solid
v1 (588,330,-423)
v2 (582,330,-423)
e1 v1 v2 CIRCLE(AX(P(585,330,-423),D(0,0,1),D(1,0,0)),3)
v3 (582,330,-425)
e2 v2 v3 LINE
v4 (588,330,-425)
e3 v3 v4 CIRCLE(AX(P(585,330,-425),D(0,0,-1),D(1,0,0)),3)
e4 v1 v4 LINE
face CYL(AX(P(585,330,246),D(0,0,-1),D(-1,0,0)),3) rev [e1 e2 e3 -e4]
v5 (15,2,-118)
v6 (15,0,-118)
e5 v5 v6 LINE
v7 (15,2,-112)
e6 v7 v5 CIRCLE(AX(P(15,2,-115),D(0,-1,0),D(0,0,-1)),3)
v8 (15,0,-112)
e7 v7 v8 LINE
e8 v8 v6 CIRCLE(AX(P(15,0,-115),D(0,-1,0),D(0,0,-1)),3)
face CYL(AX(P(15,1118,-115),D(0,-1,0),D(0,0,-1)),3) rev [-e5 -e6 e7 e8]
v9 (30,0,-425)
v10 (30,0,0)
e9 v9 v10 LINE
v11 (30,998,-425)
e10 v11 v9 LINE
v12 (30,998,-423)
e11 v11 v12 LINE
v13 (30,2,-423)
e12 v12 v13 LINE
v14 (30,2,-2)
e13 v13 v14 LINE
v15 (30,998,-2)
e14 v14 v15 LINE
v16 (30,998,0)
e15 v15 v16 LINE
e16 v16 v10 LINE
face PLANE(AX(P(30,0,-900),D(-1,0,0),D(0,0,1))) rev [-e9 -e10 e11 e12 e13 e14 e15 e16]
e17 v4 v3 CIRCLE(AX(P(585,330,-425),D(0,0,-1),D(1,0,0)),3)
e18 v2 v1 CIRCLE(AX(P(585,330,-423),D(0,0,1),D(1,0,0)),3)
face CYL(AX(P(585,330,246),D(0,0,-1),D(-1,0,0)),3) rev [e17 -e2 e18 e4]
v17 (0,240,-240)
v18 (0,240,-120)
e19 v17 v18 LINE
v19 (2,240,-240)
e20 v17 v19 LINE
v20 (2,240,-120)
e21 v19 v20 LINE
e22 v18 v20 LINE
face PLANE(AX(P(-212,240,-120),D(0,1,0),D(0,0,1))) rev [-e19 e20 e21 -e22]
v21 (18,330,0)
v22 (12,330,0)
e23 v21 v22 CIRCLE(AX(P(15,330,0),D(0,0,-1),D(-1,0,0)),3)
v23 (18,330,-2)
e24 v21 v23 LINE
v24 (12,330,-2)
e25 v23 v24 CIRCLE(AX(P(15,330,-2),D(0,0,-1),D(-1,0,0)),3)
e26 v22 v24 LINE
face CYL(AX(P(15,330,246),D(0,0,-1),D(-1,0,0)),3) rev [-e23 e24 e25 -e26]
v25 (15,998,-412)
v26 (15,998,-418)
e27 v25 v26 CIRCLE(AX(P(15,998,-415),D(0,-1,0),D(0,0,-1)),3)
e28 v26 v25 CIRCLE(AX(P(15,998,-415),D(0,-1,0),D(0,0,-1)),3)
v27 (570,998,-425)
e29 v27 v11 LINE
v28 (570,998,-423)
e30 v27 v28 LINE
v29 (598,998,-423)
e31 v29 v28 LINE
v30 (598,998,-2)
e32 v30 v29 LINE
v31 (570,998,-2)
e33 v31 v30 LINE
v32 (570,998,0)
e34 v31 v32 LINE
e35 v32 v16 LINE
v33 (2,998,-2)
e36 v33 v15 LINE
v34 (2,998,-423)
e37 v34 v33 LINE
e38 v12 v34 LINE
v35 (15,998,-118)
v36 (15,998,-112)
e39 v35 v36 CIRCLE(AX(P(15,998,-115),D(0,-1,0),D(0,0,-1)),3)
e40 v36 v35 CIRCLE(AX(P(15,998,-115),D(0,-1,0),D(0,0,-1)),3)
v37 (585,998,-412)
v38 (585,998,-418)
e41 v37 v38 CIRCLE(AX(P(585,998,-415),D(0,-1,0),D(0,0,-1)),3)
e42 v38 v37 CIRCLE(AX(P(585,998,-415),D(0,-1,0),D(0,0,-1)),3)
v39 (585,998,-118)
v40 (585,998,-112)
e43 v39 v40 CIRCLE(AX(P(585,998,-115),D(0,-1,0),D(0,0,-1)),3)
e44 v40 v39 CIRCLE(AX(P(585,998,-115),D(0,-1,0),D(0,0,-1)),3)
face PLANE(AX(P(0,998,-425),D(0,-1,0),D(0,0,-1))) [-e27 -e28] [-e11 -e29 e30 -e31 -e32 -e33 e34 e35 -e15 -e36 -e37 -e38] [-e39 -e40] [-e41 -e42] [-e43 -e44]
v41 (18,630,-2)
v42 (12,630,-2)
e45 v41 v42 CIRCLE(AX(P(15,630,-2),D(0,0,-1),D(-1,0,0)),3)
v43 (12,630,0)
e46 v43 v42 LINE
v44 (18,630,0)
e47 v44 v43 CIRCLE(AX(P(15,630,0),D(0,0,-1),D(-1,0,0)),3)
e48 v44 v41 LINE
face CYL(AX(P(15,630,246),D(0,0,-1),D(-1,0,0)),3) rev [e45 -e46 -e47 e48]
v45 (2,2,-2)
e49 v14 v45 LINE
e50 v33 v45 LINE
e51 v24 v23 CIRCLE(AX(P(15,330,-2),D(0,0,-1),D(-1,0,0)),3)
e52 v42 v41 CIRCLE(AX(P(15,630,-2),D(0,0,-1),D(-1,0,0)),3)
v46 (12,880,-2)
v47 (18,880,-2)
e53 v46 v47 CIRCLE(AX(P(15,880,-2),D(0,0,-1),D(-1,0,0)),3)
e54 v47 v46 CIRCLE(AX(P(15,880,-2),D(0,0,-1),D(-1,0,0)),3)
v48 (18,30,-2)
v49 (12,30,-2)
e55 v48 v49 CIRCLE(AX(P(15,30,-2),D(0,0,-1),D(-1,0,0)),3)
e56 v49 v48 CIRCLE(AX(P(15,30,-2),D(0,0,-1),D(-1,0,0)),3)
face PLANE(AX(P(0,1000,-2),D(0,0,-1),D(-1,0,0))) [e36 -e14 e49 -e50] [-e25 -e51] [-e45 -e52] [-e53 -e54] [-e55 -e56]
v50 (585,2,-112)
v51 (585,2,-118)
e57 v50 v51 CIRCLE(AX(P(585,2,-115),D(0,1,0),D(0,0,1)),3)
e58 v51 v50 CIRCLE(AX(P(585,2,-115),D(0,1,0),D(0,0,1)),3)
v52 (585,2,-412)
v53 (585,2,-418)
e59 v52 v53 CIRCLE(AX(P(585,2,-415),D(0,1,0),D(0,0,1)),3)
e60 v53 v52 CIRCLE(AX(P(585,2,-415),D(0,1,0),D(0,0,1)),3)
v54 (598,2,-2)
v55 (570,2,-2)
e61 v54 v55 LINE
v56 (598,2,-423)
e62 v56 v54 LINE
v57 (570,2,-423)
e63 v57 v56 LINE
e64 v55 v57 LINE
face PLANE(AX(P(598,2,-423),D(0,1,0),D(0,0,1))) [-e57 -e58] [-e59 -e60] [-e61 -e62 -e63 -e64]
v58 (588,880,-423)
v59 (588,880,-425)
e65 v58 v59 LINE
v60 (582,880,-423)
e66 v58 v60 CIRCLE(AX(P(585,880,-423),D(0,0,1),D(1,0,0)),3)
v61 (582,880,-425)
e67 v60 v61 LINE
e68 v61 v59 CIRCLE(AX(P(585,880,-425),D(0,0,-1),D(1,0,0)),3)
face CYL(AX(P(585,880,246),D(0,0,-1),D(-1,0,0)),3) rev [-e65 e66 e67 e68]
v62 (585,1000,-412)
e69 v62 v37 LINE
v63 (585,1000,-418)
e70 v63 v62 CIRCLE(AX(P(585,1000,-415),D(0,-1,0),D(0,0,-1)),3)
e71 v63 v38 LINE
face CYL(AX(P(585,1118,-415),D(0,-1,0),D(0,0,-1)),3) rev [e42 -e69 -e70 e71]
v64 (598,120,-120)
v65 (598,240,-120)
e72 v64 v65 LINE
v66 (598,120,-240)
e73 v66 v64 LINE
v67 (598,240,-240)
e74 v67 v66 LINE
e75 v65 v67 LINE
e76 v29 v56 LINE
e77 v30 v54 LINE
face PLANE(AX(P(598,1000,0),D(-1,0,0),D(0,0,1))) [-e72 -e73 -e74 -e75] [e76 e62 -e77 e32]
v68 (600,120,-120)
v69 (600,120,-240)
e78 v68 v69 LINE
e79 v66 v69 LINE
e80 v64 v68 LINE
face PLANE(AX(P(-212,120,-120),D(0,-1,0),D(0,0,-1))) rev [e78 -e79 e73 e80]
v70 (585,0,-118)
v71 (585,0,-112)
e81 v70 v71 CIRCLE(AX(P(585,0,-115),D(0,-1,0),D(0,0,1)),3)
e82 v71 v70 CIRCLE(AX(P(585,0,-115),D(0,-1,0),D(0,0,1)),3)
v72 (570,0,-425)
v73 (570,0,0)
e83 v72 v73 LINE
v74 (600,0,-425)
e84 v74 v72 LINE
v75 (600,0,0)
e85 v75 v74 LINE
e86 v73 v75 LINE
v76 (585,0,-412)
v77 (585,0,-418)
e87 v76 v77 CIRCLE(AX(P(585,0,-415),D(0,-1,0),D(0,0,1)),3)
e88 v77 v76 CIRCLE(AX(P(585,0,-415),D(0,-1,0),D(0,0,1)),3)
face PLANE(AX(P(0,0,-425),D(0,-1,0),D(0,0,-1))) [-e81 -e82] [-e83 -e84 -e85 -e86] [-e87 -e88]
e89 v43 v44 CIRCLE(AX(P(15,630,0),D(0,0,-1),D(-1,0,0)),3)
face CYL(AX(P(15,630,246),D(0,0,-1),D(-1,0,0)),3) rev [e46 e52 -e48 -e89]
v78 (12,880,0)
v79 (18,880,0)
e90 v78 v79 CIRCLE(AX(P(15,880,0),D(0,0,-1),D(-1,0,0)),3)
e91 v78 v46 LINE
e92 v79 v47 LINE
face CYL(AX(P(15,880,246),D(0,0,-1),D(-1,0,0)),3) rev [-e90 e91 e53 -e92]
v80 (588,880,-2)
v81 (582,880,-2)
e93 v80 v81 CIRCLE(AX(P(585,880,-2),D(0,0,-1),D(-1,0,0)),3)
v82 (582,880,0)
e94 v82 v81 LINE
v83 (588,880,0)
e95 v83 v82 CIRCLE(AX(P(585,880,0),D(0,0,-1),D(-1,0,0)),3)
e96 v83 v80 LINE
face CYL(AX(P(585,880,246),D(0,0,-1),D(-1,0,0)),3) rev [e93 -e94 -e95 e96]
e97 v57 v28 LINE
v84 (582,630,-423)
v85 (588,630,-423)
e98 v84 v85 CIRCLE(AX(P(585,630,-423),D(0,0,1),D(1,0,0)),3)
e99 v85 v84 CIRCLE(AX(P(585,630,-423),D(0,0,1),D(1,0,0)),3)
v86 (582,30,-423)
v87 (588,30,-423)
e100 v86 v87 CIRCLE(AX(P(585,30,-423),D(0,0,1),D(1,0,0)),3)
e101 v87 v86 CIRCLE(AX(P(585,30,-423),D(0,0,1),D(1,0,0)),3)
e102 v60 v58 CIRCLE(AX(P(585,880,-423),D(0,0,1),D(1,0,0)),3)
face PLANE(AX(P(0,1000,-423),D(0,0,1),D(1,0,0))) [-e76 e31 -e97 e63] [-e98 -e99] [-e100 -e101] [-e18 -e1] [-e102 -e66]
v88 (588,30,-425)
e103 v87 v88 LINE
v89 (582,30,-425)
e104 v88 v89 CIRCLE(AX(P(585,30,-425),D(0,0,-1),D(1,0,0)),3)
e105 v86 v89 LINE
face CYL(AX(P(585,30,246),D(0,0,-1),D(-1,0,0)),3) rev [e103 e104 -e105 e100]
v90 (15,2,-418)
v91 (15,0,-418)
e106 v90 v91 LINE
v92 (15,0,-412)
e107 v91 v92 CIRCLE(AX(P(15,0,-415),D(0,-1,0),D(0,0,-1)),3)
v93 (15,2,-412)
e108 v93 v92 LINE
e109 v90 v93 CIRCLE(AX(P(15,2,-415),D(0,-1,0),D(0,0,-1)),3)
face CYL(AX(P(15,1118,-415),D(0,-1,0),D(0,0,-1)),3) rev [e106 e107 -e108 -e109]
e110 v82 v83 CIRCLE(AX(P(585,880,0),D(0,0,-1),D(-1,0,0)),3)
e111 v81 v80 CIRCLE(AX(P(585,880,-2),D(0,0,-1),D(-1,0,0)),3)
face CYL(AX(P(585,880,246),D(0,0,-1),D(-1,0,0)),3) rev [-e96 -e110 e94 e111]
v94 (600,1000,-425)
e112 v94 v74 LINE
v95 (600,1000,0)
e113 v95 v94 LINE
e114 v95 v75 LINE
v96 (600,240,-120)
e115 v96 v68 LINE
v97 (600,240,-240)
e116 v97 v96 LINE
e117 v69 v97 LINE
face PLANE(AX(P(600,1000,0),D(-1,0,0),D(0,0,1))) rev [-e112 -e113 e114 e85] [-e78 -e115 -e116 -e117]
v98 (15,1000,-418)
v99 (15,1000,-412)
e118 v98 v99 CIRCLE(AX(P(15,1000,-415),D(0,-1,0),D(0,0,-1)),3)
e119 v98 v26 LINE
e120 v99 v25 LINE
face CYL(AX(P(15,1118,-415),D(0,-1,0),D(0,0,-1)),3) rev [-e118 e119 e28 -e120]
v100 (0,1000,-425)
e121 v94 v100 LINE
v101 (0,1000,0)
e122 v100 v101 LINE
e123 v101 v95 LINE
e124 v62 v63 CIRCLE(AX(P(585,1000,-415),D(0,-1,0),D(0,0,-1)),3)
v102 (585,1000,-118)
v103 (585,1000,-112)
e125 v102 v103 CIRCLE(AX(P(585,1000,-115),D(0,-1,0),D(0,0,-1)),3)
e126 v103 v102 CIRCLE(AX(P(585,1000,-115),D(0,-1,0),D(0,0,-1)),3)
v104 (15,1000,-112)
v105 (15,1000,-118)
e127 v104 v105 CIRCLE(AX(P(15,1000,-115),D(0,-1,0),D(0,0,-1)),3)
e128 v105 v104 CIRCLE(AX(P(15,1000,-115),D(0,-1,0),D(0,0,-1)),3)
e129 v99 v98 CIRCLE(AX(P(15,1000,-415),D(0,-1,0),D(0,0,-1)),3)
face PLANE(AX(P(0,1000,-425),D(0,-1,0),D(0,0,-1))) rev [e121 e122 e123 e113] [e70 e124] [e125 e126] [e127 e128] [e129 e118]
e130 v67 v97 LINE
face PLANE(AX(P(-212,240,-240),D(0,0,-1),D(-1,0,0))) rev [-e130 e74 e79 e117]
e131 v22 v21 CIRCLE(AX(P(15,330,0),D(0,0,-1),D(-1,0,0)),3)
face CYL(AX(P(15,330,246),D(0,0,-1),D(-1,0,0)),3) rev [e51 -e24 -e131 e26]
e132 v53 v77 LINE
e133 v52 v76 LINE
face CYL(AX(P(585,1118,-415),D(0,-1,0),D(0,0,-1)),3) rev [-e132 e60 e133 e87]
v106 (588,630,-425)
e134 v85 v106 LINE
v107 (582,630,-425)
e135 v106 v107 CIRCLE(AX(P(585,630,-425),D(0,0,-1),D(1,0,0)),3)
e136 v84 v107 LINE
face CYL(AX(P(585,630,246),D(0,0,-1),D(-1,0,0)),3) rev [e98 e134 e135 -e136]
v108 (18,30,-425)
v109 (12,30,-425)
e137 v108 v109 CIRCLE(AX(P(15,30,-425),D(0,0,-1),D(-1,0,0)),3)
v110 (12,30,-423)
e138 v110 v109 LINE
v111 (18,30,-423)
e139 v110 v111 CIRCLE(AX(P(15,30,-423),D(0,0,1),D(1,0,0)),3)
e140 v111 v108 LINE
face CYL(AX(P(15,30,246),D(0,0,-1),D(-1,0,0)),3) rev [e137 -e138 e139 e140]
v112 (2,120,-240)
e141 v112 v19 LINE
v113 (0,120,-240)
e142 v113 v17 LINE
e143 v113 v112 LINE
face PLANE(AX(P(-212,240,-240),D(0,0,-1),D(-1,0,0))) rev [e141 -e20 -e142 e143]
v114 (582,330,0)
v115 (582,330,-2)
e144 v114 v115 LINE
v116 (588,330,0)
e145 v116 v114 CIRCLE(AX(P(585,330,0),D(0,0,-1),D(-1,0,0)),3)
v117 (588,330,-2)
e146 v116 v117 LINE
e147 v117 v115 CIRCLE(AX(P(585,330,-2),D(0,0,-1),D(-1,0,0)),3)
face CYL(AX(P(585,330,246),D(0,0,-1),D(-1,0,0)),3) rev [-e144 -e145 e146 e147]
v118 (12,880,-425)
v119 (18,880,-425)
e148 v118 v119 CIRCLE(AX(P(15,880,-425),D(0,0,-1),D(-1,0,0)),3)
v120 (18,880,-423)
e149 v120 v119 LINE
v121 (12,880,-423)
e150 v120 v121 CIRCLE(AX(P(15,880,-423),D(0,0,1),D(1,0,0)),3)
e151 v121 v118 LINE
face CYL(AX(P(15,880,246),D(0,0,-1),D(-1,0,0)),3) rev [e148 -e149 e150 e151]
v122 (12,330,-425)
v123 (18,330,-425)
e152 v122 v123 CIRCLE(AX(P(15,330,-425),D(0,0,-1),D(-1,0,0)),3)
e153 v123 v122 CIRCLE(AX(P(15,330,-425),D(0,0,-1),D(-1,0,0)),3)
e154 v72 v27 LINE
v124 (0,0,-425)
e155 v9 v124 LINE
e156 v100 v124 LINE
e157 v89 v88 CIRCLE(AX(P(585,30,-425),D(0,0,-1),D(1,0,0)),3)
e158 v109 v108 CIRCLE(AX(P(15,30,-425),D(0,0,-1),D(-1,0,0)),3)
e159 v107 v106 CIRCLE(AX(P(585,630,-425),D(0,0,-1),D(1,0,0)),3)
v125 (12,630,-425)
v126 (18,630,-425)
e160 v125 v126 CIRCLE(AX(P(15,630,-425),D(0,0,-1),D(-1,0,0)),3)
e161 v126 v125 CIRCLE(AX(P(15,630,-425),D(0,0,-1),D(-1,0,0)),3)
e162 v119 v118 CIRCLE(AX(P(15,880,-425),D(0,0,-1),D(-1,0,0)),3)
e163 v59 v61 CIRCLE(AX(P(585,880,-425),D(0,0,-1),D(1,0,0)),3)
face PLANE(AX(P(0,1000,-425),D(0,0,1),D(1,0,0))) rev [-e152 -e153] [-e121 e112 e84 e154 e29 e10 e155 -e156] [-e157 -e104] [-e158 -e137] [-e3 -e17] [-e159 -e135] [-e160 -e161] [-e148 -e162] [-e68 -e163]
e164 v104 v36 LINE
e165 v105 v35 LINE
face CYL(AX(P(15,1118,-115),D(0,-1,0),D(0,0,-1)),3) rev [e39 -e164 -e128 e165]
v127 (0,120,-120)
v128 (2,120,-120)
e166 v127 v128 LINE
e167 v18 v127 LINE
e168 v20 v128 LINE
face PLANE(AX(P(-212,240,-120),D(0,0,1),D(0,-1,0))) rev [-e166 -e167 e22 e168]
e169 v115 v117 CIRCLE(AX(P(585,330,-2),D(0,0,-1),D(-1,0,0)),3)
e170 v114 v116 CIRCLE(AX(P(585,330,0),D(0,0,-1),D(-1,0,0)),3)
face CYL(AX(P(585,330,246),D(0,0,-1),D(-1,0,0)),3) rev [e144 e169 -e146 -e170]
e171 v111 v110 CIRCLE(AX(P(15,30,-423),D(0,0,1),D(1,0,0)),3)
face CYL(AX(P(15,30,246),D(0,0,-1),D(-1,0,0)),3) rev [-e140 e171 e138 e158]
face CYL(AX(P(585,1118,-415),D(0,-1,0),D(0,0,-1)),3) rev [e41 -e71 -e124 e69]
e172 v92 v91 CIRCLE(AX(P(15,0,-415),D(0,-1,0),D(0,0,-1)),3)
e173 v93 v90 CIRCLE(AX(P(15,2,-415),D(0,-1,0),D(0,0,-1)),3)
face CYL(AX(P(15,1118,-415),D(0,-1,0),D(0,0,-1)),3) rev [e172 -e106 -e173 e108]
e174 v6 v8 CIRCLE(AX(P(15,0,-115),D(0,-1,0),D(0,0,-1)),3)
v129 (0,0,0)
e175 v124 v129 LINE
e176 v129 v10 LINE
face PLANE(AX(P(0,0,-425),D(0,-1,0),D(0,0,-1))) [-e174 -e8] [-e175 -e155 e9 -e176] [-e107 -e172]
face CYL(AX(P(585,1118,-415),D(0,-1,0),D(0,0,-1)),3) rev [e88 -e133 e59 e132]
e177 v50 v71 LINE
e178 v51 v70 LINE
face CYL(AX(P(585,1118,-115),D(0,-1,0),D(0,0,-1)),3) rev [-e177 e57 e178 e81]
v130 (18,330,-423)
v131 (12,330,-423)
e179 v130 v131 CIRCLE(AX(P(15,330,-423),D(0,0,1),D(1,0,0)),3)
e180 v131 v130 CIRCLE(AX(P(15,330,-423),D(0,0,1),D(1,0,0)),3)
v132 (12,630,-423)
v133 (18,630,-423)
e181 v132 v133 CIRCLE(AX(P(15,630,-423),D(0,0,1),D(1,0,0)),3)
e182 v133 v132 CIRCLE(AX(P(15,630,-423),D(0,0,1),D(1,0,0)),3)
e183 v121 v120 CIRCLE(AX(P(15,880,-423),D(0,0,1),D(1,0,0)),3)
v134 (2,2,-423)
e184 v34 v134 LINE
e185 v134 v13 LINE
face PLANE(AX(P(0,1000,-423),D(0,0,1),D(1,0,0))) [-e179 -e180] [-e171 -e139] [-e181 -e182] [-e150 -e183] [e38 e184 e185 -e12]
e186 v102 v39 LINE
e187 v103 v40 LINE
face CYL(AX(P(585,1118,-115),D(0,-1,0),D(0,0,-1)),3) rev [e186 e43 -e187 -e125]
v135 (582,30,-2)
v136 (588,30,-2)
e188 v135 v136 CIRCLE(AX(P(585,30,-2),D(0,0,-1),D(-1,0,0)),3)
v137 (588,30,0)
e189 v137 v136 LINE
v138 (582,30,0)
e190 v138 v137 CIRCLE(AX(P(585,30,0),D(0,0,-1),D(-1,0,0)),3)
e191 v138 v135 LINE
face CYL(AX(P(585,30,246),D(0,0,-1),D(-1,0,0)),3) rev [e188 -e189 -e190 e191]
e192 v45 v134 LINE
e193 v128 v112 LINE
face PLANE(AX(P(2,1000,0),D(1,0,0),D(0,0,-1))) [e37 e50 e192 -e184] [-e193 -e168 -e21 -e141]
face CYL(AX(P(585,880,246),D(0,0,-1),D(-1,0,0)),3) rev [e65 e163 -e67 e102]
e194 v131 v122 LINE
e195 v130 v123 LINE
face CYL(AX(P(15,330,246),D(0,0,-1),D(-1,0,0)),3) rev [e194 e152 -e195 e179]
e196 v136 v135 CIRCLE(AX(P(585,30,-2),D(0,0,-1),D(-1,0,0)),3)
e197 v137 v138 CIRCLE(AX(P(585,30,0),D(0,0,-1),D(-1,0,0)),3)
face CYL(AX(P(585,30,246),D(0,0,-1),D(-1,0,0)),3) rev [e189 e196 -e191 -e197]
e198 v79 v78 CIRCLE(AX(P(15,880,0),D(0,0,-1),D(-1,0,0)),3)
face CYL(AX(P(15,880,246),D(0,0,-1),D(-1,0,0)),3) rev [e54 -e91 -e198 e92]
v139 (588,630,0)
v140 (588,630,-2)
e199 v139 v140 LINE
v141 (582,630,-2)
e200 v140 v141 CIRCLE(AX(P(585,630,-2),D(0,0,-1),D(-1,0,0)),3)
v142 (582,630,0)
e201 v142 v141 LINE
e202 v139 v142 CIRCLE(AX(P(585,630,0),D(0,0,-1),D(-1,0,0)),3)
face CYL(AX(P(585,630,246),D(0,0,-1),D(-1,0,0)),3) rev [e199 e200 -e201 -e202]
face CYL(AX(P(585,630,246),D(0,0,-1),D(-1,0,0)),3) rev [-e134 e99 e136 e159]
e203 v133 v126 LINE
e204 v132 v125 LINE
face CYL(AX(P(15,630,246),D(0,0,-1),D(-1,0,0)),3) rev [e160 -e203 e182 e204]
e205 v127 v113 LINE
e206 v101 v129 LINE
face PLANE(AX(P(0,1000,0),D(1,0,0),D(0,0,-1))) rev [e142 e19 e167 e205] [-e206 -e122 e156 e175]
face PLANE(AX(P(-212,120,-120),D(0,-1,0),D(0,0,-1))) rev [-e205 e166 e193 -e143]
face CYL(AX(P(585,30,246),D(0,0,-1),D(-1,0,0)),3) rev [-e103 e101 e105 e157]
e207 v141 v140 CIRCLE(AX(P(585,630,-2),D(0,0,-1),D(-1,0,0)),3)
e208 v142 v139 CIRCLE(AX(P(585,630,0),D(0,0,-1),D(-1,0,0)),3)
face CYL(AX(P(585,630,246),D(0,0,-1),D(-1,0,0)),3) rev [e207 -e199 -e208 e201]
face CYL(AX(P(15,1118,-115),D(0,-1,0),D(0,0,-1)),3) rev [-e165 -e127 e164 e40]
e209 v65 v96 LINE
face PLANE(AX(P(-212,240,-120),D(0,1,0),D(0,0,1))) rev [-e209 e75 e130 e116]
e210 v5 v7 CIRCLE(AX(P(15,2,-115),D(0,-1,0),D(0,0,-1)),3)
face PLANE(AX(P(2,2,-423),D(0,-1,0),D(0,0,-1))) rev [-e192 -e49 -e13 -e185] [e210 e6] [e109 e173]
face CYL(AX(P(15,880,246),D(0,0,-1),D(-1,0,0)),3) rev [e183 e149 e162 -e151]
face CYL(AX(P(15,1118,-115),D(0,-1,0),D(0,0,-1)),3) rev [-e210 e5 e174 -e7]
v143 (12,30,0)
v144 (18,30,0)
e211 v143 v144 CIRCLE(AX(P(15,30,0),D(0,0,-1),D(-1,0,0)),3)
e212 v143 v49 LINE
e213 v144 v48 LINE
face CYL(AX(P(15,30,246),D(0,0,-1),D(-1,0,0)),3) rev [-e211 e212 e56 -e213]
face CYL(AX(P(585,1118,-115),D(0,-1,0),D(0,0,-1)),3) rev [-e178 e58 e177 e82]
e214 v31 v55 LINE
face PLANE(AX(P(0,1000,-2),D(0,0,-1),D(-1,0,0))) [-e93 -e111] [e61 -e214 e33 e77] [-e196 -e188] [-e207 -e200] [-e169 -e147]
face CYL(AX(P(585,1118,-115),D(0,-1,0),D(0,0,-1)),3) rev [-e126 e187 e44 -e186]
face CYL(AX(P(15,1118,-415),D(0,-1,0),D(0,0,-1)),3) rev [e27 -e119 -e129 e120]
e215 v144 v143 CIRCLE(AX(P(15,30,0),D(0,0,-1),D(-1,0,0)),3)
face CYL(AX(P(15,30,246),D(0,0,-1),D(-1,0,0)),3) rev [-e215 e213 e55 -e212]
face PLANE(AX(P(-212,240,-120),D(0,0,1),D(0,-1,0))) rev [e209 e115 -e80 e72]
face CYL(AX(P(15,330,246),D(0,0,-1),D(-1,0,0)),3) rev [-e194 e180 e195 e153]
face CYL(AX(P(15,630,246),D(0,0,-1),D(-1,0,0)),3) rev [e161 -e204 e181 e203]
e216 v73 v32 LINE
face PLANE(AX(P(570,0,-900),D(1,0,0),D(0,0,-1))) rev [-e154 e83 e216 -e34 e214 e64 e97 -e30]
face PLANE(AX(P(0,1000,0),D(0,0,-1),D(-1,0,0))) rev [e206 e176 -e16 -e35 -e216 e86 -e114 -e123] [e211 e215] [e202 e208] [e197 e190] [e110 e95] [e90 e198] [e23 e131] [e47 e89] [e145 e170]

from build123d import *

# Parameters (mm, degrees)
SKETCH_1_W          = 600
SKETCH_1_H          = 425
EXTRUDE_1_DEPTH     = 1000
SHELL_2_T           = -2
SKETCH_2_W          = 540
SKETCH_2_H          = 998
CUT_EXTRUDE_1_DEPTH = 900
SKETCH_5_W          = 28
SKETCH_5_H          = 421
EXTRUDE_2_DEPTH     = 2
SKETCH_6_W          = 120
SKETCH_6_H          = 120
CUT_EXTRUDE_3_DEPTH = 812
SKETCH_7_R          = 3
CUT_EXTRUDE_4_DEPTH = 1118
SKETCH_8_R          = 3
CUT_EXTRUDE_5_DEPTH = 671


with BuildPart() as part:
    # 草图1 → 凸台-拉伸1 (new body)
    with BuildSketch(Plane(origin=(0, 0, 0), x_dir=(1, 0, 0), z_dir=(0, 1, 0))):
        with Locations((300, 212.5)):
            Rectangle(SKETCH_1_W, SKETCH_1_H)
    extrude(amount=EXTRUDE_1_DEPTH)

    # 抽壳2
    shell_2_openings = [part.faces().sort_by_distance(p)[0] for p in [
        (300, 0, -212.5),
    ]]
    offset(amount=SHELL_2_T, openings=shell_2_openings, kind=Kind.INTERSECTION)

    # 草图2 → 切除-拉伸1 (cut)
    with BuildSketch(Plane.XY):
        with Locations((300, 499)):
            Rectangle(SKETCH_2_W, SKETCH_2_H)
    extrude(amount=-CUT_EXTRUDE_1_DEPTH, mode=Mode.SUBTRACT)

    # 草图5 → 凸台-拉伸2 (add)
    with BuildSketch(Plane.XZ):
        with Locations((16, -212.5)):
            Rectangle(SKETCH_5_W, SKETCH_5_H)
        with Locations((584, -212.5)):
            Rectangle(SKETCH_5_W, SKETCH_5_H)
    extrude(amount=-EXTRUDE_2_DEPTH)

    # 草图6 → 切除-拉伸3 (cut)
    with BuildSketch(Plane(origin=(600, 0, 0), x_dir=(0, 0, -1), z_dir=(1, 0, 0))):
        with Locations((180, 180)):
            Rectangle(SKETCH_6_W, SKETCH_6_H)
    extrude(amount=-CUT_EXTRUDE_3_DEPTH, mode=Mode.SUBTRACT)

    # 草图7 → 切除-拉伸4 (cut)
    with BuildSketch(Plane.XZ):
        with Locations(Location((15, -115, 0), (0, 0, 270))):
            Circle(SKETCH_7_R)
        with Locations(Location((585, -415, 0), (0, 0, 90))):
            Circle(SKETCH_7_R)
        with Locations(Location((15, -415, 0), (0, 0, 270))):
            Circle(SKETCH_7_R)
        with Locations(Location((585, -115, 0), (0, 0, 90))):
            Circle(SKETCH_7_R)
    extrude(amount=-CUT_EXTRUDE_4_DEPTH, mode=Mode.SUBTRACT)

    # 草图8 → 切除-拉伸5 (cut)
    with BuildSketch(Plane(origin=(0, 0, -425), x_dir=(-1, 0, 0), z_dir=(0, 0, -1))):
        with Locations((-15, 30)):
            Circle(SKETCH_8_R)
        with Locations((-15, 330)):
            Circle(SKETCH_8_R)
        with Locations((-15, 630)):
            Circle(SKETCH_8_R)
        with Locations(Location((-585, 30, 0), (0, 0, 180))):
            Circle(SKETCH_8_R)
        with Locations(Location((-585, 330, 0), (0, 0, 180))):
            Circle(SKETCH_8_R)
        with Locations((-15, 880)):
            Circle(SKETCH_8_R)
        with Locations(Location((-585, 630, 0), (0, 0, 180))):
            Circle(SKETCH_8_R)
        with Locations(Location((-585, 880, 0), (0, 0, 180))):
            Circle(SKETCH_8_R)
    extrude(amount=-CUT_EXTRUDE_5_DEPTH, mode=Mode.SUBTRACT)


solid = part.part
